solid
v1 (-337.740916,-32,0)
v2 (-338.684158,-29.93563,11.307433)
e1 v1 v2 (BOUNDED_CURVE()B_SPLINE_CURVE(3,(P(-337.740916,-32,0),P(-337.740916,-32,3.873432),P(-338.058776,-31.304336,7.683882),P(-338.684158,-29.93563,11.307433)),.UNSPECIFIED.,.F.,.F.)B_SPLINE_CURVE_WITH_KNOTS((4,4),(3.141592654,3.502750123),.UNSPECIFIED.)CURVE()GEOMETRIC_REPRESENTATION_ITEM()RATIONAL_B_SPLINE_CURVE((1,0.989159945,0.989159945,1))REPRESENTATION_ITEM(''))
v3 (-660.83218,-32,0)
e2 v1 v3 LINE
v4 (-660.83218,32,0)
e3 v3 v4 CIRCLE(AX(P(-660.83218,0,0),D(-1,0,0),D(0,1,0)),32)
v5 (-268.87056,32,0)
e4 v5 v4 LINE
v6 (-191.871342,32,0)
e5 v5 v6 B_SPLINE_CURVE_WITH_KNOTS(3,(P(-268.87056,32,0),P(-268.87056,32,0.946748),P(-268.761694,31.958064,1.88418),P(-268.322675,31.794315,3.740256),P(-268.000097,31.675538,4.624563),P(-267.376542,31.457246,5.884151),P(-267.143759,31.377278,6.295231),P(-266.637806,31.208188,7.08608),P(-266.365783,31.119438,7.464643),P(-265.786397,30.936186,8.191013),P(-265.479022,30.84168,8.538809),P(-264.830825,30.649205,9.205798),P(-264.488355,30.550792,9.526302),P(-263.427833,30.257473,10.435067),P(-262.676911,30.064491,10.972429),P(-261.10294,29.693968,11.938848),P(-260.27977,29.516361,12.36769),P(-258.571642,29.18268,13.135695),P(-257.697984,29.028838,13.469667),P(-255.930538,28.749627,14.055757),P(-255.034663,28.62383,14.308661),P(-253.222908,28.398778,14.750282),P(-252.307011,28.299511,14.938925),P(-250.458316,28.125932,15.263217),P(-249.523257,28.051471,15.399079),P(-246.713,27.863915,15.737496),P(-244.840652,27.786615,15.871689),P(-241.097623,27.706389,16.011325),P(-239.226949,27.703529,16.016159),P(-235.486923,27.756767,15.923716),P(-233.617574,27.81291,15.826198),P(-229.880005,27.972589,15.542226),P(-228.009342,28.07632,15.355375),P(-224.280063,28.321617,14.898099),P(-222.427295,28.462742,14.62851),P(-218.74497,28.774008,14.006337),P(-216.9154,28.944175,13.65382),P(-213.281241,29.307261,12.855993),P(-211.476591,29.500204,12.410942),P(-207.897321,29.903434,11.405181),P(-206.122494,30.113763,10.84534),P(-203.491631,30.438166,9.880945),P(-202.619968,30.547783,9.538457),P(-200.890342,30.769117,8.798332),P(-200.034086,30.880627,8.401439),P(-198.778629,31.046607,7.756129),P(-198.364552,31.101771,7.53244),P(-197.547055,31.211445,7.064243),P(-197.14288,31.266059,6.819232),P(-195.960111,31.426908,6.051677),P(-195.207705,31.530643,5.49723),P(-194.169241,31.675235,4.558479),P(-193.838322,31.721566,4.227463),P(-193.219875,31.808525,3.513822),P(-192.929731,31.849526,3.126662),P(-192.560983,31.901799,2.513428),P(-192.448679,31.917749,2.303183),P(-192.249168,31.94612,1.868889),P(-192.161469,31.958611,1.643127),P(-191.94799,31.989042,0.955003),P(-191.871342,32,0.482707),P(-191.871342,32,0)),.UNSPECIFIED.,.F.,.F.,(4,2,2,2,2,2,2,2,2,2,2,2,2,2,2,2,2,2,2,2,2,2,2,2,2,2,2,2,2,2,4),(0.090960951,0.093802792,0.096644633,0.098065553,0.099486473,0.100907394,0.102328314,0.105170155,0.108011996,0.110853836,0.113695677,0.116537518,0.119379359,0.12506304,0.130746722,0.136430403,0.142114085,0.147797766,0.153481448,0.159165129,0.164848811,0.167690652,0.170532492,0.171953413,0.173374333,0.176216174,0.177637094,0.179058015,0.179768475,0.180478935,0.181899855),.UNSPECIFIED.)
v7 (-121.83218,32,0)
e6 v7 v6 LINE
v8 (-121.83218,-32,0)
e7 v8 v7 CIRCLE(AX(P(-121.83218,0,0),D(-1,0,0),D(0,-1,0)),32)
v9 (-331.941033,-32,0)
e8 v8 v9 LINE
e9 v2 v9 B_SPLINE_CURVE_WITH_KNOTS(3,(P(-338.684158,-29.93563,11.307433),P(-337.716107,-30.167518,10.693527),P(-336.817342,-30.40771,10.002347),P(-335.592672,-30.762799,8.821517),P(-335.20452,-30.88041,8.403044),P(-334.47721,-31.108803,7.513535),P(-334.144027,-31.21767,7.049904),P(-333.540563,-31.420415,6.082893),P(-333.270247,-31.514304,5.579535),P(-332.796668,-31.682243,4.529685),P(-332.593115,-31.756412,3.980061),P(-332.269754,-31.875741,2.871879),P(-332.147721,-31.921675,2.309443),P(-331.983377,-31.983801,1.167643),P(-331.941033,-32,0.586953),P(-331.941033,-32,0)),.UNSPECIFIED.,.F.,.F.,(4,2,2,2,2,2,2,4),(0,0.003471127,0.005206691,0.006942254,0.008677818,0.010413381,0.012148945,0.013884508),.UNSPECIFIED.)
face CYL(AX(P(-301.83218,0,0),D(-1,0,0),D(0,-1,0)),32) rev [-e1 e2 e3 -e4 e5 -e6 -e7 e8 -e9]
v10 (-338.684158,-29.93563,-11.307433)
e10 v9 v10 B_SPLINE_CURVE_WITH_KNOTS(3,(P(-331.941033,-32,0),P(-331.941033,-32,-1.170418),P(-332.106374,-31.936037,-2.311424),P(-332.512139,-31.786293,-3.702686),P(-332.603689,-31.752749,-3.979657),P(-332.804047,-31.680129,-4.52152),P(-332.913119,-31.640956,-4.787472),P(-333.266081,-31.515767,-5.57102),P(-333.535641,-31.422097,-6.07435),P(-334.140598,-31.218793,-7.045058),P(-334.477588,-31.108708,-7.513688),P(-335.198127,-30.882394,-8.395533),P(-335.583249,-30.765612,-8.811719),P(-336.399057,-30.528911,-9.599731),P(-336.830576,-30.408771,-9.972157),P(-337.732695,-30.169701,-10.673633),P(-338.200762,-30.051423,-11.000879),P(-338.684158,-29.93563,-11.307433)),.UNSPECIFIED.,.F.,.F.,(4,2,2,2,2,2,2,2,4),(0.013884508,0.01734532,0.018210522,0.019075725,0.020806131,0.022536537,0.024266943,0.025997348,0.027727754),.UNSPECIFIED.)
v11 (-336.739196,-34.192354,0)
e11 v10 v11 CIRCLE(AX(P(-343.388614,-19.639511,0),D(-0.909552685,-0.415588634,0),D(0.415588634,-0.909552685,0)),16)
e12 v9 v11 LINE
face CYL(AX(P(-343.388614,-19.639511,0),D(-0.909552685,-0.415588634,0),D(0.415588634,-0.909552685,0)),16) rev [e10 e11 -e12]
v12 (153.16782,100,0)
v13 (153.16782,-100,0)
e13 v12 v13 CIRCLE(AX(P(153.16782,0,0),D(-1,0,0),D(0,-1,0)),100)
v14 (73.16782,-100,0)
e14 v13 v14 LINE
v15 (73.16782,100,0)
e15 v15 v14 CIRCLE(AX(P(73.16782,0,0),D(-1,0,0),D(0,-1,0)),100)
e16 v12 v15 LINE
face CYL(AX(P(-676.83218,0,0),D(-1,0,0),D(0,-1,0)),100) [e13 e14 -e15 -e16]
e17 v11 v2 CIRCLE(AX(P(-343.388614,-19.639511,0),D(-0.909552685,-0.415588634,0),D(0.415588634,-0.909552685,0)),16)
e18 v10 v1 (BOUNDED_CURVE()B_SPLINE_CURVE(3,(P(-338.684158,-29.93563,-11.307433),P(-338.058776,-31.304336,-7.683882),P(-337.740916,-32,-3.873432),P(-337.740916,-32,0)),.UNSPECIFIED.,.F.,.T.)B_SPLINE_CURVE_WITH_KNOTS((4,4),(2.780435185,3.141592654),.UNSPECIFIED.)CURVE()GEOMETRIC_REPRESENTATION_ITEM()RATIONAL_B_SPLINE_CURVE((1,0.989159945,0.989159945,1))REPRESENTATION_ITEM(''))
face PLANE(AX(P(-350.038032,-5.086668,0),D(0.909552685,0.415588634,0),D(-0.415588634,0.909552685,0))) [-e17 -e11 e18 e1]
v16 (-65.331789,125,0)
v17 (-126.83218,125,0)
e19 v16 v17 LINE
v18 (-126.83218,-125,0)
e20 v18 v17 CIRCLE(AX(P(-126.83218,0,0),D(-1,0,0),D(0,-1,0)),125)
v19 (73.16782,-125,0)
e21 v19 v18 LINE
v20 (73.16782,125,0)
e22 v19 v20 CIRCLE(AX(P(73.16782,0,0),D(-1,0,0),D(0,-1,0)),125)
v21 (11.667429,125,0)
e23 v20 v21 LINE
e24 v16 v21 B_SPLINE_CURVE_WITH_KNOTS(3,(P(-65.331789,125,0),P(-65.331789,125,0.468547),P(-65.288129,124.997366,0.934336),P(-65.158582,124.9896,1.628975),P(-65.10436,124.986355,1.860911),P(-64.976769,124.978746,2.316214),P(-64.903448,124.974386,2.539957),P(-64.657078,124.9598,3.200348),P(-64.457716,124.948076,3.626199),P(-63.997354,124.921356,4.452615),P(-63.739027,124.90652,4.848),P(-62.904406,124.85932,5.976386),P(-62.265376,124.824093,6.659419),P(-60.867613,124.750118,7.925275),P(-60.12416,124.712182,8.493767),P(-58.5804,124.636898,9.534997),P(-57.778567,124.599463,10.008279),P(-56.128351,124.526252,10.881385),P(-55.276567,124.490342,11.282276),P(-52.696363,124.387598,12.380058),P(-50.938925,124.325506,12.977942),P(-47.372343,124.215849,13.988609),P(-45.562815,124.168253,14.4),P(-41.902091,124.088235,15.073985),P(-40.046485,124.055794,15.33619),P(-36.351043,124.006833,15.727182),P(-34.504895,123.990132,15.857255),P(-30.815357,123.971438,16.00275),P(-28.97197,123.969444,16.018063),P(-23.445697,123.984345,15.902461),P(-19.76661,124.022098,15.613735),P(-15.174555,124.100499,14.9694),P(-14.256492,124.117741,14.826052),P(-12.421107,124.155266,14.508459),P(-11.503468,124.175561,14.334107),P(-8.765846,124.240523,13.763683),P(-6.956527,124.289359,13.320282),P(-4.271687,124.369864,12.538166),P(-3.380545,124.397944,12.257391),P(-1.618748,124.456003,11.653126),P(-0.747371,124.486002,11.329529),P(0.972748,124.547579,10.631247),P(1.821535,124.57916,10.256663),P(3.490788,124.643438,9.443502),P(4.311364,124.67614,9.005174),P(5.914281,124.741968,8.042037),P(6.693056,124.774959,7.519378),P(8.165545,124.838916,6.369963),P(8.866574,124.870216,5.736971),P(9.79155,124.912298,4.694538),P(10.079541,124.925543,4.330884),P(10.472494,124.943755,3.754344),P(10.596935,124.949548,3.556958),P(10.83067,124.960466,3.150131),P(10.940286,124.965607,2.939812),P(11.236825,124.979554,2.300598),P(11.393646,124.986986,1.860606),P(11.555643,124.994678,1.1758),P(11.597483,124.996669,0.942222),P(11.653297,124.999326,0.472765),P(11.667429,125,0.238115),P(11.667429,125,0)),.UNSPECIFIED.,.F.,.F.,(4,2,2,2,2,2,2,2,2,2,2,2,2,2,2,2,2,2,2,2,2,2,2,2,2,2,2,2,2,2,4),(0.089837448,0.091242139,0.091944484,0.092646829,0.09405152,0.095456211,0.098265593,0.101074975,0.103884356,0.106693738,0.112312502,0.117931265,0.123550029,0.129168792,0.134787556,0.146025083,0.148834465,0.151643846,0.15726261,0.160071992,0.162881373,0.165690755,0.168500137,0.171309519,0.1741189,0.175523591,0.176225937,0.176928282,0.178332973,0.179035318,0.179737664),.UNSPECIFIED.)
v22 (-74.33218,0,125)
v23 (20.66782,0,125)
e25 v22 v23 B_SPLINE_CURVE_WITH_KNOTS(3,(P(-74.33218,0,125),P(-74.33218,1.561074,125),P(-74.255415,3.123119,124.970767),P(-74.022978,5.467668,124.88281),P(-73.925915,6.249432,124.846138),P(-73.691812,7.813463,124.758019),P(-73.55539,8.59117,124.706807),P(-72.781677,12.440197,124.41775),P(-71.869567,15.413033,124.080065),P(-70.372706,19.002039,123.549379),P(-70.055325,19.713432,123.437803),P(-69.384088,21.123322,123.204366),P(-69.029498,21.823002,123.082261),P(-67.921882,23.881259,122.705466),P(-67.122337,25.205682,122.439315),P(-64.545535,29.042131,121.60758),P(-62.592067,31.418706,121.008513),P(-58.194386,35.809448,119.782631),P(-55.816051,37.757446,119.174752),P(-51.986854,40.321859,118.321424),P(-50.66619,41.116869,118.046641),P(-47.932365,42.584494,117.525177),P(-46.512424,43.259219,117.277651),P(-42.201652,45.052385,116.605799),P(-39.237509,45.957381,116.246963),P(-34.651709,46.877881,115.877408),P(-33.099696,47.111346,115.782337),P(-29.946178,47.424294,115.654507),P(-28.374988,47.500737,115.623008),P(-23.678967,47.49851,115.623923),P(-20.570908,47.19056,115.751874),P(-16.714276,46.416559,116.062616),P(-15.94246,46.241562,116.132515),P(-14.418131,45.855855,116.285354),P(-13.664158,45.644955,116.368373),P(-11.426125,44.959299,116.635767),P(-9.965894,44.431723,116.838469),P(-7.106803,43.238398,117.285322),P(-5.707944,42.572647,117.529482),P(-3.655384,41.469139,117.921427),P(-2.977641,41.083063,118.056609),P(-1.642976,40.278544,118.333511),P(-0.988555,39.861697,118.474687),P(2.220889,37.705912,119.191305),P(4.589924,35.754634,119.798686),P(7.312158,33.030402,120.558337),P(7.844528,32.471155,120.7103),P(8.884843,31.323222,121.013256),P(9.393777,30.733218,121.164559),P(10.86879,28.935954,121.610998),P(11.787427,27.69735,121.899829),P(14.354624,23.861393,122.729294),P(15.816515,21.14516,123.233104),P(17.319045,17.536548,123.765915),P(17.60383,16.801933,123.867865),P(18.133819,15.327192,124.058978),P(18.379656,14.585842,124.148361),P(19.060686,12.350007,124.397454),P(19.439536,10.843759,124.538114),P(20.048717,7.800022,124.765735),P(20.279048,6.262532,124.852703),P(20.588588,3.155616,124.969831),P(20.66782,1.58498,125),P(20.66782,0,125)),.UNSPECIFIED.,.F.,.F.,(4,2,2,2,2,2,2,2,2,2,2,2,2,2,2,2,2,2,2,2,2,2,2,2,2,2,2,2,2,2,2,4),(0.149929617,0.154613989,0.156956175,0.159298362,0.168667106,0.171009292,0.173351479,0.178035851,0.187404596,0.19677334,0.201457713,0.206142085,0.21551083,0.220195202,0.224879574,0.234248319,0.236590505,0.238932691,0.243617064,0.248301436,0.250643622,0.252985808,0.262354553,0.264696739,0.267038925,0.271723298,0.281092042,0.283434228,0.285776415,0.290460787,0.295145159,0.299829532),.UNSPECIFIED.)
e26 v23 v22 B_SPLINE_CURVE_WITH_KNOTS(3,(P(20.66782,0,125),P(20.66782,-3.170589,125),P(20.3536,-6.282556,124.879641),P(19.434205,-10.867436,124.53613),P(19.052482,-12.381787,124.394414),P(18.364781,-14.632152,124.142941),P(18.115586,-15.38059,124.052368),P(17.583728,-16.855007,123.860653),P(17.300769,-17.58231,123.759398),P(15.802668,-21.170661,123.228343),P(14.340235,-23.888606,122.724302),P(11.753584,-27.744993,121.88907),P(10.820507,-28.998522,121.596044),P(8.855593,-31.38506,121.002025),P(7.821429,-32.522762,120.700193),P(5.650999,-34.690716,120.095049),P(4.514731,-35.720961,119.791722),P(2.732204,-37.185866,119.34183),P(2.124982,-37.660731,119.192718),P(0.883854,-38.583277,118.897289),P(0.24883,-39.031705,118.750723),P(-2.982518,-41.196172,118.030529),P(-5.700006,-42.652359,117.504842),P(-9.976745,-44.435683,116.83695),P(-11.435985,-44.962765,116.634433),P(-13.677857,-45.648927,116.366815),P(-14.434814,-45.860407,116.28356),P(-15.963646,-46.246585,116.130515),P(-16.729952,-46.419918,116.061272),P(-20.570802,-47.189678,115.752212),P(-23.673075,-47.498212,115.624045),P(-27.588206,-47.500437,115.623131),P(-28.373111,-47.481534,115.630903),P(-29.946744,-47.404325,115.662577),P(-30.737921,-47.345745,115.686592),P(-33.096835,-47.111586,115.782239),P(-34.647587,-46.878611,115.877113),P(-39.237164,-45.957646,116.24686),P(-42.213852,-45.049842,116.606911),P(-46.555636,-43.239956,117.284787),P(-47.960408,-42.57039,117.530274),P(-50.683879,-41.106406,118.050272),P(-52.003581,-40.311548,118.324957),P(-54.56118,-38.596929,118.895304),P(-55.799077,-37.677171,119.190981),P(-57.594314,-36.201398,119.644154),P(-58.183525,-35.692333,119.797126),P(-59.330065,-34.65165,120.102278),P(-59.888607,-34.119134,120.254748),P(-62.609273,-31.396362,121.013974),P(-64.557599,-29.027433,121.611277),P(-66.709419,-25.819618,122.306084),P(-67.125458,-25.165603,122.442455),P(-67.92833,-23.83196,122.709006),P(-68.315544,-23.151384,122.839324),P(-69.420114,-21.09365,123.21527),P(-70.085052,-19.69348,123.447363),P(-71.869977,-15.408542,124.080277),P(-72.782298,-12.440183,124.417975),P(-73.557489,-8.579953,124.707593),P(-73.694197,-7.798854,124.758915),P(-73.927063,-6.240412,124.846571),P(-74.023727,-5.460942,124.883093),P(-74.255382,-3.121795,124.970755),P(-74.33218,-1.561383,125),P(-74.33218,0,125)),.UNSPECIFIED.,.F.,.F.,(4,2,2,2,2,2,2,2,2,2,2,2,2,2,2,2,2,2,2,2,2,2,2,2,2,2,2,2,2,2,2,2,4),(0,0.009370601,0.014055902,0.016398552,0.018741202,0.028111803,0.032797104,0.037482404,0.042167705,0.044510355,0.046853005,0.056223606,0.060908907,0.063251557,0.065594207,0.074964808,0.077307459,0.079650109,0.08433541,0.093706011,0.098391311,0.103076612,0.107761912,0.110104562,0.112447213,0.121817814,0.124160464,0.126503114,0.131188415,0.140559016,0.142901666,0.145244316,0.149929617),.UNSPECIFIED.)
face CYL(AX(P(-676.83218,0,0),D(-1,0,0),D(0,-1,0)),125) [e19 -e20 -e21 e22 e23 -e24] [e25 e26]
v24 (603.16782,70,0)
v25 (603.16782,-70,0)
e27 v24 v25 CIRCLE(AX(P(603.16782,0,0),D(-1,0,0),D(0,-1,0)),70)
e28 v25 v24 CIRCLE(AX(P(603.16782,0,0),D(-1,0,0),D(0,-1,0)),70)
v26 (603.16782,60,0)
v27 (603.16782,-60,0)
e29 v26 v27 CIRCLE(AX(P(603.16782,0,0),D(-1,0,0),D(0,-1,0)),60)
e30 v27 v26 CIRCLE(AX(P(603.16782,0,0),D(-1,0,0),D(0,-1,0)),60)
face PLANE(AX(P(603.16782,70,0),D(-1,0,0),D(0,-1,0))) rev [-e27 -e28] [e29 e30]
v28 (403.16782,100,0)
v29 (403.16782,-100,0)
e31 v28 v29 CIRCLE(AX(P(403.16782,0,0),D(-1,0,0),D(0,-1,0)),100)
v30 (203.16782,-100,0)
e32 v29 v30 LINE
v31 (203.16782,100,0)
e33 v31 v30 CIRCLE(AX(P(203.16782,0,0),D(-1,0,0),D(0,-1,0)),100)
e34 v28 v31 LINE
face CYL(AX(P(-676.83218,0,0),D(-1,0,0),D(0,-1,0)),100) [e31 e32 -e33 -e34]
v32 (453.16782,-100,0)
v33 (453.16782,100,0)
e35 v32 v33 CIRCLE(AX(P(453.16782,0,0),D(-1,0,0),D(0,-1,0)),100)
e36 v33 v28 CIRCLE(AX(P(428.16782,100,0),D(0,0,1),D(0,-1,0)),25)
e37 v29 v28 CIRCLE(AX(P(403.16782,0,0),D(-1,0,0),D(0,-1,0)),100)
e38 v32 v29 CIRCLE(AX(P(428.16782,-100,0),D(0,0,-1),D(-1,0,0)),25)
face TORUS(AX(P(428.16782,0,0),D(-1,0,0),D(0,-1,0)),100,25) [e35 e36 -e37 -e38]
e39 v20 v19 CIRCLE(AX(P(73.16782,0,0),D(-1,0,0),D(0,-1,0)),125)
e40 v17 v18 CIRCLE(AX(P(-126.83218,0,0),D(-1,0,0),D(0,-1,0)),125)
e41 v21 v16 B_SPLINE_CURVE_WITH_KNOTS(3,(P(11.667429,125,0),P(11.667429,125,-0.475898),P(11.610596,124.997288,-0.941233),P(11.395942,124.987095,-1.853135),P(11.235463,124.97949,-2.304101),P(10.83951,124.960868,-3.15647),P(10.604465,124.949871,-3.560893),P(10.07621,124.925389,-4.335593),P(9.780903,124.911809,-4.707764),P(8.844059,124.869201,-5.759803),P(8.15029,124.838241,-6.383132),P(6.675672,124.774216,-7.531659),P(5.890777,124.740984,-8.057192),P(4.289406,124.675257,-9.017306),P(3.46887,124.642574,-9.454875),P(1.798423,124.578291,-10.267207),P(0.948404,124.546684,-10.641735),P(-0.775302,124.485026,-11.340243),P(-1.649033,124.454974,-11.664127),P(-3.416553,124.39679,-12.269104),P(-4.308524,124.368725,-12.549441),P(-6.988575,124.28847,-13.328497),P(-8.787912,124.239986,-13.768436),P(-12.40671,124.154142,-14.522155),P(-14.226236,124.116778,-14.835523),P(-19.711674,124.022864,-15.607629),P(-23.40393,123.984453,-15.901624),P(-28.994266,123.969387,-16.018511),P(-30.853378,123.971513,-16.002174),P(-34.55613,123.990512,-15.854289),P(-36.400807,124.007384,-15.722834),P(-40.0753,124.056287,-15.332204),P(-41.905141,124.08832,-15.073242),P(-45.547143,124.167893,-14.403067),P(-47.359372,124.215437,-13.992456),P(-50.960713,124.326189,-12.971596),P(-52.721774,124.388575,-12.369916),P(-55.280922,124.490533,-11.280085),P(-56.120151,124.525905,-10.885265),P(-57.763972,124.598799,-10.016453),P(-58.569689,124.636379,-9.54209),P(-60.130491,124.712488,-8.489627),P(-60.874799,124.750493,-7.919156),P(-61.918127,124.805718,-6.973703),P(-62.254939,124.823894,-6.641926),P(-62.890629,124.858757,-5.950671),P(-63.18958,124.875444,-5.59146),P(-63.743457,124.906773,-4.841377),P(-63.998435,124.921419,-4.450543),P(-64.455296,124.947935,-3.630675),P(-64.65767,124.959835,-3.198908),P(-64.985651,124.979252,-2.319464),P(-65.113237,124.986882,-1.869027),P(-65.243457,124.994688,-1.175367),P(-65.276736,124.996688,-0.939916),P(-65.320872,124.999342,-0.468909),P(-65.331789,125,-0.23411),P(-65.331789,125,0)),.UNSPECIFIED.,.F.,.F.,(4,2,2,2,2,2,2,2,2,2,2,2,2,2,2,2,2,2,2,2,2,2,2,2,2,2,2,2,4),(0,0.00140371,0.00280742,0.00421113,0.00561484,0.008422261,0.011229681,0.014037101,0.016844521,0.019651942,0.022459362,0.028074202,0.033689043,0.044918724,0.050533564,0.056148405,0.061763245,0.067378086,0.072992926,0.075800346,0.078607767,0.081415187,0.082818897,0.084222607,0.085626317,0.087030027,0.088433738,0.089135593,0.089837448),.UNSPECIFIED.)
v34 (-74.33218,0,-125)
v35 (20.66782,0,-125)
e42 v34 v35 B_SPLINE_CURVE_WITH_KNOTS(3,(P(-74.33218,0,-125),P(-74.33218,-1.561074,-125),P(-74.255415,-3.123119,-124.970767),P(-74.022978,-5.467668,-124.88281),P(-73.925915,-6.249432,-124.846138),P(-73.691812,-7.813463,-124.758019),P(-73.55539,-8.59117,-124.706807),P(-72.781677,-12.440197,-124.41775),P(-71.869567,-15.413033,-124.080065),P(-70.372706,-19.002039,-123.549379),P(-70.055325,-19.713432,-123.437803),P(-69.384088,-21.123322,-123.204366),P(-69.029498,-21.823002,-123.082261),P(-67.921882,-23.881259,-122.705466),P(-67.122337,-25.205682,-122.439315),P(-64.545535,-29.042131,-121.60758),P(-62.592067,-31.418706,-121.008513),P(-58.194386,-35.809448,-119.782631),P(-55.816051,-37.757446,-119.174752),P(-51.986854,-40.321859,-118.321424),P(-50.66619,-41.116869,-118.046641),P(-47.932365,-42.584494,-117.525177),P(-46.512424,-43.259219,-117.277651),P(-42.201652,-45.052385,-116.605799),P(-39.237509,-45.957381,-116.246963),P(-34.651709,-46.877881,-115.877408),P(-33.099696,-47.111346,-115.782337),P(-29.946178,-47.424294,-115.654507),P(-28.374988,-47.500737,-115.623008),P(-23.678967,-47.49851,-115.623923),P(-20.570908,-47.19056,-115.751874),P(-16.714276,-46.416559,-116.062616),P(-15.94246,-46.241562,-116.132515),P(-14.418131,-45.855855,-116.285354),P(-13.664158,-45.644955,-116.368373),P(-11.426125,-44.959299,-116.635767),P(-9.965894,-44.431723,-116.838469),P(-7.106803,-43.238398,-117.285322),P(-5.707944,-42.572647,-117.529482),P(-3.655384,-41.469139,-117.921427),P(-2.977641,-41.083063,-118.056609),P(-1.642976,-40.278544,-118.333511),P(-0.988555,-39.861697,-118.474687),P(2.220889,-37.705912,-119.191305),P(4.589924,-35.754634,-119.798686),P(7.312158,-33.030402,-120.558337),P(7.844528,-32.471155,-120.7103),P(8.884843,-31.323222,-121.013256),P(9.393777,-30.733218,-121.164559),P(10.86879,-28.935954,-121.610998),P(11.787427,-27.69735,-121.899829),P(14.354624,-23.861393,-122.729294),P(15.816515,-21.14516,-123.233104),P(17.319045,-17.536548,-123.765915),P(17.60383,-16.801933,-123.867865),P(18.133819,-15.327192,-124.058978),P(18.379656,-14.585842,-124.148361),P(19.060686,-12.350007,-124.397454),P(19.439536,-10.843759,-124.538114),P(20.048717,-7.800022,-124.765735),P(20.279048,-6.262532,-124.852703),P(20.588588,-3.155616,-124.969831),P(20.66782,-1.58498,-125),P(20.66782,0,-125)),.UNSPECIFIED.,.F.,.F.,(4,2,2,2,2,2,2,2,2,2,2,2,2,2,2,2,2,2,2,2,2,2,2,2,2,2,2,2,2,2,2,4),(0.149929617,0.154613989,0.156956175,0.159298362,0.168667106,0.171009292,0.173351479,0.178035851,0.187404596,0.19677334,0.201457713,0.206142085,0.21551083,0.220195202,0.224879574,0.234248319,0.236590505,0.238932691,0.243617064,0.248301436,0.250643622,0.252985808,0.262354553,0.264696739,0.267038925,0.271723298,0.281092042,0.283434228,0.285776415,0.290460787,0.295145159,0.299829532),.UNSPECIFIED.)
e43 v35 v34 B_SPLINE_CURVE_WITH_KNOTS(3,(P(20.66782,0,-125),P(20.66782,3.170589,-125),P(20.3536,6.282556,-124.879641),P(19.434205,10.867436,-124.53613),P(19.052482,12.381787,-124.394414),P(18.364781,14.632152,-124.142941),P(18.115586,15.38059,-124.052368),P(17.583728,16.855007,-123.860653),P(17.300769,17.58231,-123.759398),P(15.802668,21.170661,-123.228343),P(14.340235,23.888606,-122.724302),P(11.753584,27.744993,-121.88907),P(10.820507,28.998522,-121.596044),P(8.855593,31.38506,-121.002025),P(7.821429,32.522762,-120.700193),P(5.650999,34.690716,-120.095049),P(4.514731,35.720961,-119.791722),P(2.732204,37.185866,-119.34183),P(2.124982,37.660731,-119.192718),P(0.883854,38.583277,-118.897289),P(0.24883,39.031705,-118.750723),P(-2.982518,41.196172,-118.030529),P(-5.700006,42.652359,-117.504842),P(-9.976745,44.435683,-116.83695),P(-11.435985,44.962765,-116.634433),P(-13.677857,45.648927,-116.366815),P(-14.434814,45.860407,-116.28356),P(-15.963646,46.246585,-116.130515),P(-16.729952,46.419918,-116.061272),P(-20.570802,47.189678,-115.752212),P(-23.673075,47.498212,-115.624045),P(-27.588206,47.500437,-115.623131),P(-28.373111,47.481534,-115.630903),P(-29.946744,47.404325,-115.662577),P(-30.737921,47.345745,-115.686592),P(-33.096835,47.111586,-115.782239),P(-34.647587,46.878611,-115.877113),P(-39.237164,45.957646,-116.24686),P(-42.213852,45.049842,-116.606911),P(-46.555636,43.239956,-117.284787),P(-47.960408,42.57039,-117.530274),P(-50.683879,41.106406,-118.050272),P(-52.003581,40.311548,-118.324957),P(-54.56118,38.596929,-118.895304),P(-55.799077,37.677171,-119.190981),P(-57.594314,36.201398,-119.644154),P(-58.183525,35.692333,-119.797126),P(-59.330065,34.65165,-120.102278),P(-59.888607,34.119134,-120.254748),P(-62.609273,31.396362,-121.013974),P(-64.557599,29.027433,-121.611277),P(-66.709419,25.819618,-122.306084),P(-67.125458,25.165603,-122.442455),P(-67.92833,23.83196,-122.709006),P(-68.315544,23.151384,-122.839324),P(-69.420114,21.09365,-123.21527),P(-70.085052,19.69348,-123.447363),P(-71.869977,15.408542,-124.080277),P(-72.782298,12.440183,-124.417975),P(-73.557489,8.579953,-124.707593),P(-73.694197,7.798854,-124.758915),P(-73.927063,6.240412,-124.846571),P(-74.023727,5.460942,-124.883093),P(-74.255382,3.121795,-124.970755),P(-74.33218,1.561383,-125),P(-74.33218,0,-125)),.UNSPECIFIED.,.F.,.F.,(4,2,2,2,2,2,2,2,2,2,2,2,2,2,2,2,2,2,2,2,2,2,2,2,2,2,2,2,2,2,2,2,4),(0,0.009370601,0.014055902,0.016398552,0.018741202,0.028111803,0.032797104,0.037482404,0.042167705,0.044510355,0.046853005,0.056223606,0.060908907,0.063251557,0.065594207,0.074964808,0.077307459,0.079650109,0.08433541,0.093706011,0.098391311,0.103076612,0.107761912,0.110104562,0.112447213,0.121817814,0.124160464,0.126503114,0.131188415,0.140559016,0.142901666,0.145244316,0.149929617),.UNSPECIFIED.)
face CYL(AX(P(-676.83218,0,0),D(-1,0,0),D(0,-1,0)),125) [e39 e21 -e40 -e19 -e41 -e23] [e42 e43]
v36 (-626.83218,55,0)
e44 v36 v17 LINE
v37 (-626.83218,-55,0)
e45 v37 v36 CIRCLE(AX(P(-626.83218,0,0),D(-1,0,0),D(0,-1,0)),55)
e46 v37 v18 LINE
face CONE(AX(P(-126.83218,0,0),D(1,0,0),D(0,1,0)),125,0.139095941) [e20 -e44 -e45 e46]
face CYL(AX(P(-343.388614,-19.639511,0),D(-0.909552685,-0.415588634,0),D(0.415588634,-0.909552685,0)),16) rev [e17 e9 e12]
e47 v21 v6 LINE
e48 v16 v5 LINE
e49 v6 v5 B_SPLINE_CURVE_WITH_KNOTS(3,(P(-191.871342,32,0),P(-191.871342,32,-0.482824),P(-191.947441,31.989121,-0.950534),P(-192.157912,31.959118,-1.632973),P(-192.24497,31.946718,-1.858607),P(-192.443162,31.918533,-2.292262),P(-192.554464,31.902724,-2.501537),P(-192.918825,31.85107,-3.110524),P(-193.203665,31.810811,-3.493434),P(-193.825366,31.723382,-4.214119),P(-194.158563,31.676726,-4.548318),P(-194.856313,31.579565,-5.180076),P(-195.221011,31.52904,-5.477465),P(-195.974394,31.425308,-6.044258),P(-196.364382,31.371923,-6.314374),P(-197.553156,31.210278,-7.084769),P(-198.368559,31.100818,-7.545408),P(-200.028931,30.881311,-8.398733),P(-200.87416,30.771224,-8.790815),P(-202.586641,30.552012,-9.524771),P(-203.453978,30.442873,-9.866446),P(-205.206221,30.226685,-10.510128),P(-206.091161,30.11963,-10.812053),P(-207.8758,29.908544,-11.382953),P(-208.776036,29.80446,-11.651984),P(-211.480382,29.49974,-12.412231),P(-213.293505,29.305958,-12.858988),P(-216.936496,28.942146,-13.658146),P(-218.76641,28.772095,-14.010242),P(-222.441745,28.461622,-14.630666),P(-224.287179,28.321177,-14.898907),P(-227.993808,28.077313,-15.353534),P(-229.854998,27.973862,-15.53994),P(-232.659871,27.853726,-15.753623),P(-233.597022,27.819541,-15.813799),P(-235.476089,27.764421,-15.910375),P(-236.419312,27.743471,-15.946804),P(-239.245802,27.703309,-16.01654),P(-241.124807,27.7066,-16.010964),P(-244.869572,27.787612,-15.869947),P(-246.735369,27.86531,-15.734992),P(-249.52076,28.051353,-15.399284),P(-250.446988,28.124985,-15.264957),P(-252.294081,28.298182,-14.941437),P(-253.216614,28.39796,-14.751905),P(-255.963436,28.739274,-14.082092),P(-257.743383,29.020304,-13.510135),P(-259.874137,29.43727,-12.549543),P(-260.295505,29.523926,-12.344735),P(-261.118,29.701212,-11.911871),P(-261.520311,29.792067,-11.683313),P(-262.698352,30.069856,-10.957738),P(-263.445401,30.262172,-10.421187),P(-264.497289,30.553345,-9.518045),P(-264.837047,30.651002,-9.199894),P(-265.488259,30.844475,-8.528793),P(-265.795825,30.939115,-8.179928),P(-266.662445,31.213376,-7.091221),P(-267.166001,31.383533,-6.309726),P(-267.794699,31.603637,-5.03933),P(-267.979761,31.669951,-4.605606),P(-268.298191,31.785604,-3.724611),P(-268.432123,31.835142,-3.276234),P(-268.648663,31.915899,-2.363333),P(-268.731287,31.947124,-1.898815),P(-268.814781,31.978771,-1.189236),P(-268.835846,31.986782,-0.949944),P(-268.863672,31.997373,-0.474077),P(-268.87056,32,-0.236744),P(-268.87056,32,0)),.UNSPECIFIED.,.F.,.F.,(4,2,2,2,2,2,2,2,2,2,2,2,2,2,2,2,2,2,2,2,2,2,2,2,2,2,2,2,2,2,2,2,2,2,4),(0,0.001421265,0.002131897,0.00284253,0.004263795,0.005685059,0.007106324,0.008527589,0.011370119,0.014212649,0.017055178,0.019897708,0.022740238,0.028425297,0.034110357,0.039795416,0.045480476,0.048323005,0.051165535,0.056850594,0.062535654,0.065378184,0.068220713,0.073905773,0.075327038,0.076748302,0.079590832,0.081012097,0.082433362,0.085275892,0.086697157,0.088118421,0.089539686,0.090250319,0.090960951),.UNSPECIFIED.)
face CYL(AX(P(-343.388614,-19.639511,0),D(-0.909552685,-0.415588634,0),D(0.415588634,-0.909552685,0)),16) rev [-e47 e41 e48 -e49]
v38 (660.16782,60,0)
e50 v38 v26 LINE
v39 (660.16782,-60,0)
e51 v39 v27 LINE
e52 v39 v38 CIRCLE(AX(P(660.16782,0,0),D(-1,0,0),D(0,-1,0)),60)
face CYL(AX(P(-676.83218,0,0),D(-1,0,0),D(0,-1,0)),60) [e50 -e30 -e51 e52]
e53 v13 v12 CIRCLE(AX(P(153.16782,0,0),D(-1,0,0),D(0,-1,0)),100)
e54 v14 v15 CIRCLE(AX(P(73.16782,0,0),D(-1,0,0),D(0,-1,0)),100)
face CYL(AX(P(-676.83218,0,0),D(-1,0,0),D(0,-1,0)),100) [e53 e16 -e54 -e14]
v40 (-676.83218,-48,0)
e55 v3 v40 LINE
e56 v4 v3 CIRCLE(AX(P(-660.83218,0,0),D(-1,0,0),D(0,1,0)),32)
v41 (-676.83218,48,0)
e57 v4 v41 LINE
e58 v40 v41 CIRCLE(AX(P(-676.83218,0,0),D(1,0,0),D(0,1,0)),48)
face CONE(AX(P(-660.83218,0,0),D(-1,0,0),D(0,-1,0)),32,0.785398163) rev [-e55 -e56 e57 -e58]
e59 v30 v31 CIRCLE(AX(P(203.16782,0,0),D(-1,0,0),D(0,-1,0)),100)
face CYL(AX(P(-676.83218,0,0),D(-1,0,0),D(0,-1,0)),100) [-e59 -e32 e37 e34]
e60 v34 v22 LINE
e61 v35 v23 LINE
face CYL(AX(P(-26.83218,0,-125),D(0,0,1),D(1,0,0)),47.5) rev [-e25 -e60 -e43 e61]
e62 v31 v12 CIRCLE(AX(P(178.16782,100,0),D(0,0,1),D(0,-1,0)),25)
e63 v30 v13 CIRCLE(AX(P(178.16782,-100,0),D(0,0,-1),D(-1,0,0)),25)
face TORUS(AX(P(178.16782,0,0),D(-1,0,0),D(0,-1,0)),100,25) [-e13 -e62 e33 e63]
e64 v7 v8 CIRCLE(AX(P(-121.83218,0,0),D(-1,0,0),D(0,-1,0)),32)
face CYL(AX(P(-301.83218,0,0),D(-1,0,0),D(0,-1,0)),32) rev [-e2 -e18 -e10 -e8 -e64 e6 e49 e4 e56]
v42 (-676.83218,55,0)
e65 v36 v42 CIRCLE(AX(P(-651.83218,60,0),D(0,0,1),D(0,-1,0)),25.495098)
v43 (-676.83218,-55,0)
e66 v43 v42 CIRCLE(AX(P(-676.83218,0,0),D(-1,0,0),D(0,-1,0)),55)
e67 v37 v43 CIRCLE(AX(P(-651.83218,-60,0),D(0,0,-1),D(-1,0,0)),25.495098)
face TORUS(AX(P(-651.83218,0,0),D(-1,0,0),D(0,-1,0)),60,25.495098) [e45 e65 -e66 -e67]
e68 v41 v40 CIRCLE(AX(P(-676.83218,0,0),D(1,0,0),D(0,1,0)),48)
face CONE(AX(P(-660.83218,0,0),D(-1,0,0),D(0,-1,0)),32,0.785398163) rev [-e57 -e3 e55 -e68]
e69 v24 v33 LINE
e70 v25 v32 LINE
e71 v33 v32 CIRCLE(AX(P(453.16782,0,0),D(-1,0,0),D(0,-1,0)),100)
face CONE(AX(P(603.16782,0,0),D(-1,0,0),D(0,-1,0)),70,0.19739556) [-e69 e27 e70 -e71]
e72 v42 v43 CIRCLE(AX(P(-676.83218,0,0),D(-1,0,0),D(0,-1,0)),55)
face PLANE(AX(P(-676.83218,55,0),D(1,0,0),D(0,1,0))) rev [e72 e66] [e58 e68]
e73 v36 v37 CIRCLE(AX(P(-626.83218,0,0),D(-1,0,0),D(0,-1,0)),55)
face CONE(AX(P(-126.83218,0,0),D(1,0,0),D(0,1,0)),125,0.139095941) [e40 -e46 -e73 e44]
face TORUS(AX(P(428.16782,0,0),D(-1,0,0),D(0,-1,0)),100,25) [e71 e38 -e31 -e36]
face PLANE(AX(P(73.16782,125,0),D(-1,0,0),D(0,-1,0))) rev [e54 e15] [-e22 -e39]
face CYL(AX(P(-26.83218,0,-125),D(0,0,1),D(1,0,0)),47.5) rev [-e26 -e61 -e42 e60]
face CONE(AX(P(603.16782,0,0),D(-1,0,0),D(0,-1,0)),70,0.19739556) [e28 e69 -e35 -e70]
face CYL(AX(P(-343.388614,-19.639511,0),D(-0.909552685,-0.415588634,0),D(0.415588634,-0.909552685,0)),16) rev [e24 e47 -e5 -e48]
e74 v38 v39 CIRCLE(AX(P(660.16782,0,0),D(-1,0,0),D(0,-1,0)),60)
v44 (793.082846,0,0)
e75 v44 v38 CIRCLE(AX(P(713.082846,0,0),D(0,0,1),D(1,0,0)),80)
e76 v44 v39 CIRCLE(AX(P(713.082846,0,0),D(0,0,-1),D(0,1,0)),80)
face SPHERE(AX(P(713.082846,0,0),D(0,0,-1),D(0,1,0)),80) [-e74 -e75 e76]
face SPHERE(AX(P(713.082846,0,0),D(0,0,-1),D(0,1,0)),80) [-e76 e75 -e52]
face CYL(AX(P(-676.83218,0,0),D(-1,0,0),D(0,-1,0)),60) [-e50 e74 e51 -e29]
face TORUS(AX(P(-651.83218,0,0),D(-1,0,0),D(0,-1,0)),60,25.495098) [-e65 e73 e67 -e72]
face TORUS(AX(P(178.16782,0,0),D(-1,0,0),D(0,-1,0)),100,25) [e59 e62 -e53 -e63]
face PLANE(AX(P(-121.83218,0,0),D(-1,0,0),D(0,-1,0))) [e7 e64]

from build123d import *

# Parameters (mm, degrees)
BORE_SKETCH_64_R              = 32
BORE_64_X375_DEPTH            = 375
BORE_MOUTH_CHAMFER_16X45_SIZE = 16
CROSS_HOLE_CUT_DEPTH          = 813.545629788
CROSS_HOLE_CUT_DEPTH_BACK     = 813.545629788
CROSS_HOLE_SKETCH_R           = 47.5
DEEP_BORE_SKETCH_R            = 32
DEEP_BORE_CUT_555_DEPTH       = 555


with BuildPart() as part:
    # Body Profile Sketch → Revolved Body (revolve)
    with BuildSketch(Plane.XY, mode=Mode.PRIVATE) as revolved_body_sk:
        with BuildLine():
            Line((-676.832180336, 55), (-676.832180336, 0))
            Line((-676.832180336, 0), (793.082845885, 0))
            ThreePointArc((793.082845885, 0), (745.997872106, 72.915026221), (660.167819664, 60))
            Line((660.167819664, 60), (603.167819664, 60))
            Line((603.167819664, 60), (603.167819664, 70))
            Line((603.167819664, 70), (453.167819664, 100))
            ThreePointArc((453.167819664, 100), (428.167819664, 125), (403.167819664, 100))
            Line((403.167819664, 100), (203.167819664, 100))
            ThreePointArc((203.167819664, 100), (178.167819664, 125), (153.167819664, 100))
            Line((153.167819664, 100), (73.167819664, 100))
            Line((73.167819664, 100), (73.167819664, 125))
            Line((73.167819664, 125), (-126.832180336, 125))
            Line((-126.832180336, 125), (-626.832180336, 55))
            ThreePointArc((-626.832180336, 55), (-651.832180336, 85.495097568), (-676.832180336, 55))
        make_face()
    revolve(revolved_body_sk.sketch.rotate(Axis((-676.832180336, 0, 0), (1, 0, 0)), 180), axis=Axis((-676.832180336, 0, 0), (1, 0, 0)))

    # Bore Sketch Ø64 → Bore Ø64 x375 (cut)
    with BuildSketch(Plane.ZY.offset(676.832180336)):
        with Locations(Location((0, 0, 0), (0, 0, 270))):
            Circle(BORE_SKETCH_64_R)
    extrude(amount=-BORE_64_X375_DEPTH, mode=Mode.SUBTRACT)

    # Bore Mouth Chamfer 16x45
    bore_mouth_chamfer_16x45_edges = [part.edges().sort_by_distance(p)[0] for p in [
        (-676.832180336, 32, 0),
    ]]
    chamfer(bore_mouth_chamfer_16x45_edges, length=BORE_MOUTH_CHAMFER_16X45_SIZE)

    # Cross Hole Sketch → Cross Hole Cut (cut, two sides: drawn at the far end of the back side and taken through both)
    with BuildSketch(Plane.XY.offset(-CROSS_HOLE_CUT_DEPTH_BACK)):
        with Locations((-26.832180336, 0)):
            Circle(CROSS_HOLE_SKETCH_R)
    extrude(amount=CROSS_HOLE_CUT_DEPTH + CROSS_HOLE_CUT_DEPTH_BACK, mode=Mode.SUBTRACT)

    # Groove Profile Sketch → Revolved Groove Cut (revolve, cut)
    with BuildSketch(Plane.XY, mode=Mode.PRIVATE) as revolved_groove_cut_sk:
        Polygon((-350.038031958, -5.086668407), (-343.388613806, -19.639511367), (28.843028109, 150.438860479), (22.193609957, 164.99170344), align=None)
    revolve(revolved_groove_cut_sk.sketch.rotate(Axis((-343.388613806, -19.639511367, 0), (0.9095526850462128, 0.41558863449957945, 0)), 180), axis=Axis((-343.388613806, -19.639511367, 0), (0.9095526850462128, 0.41558863449957945, 0)), mode=Mode.SUBTRACT)

    # Deep Bore Sketch → Deep Bore Cut 555 (cut)
    with BuildSketch(Plane.ZY.offset(676.832180336)):
        with Locations(Location((0, 0, 0), (0, 0, 270))):
            Circle(DEEP_BORE_SKETCH_R)
    extrude(amount=-DEEP_BORE_CUT_555_DEPTH, mode=Mode.SUBTRACT)


solid = part.part
